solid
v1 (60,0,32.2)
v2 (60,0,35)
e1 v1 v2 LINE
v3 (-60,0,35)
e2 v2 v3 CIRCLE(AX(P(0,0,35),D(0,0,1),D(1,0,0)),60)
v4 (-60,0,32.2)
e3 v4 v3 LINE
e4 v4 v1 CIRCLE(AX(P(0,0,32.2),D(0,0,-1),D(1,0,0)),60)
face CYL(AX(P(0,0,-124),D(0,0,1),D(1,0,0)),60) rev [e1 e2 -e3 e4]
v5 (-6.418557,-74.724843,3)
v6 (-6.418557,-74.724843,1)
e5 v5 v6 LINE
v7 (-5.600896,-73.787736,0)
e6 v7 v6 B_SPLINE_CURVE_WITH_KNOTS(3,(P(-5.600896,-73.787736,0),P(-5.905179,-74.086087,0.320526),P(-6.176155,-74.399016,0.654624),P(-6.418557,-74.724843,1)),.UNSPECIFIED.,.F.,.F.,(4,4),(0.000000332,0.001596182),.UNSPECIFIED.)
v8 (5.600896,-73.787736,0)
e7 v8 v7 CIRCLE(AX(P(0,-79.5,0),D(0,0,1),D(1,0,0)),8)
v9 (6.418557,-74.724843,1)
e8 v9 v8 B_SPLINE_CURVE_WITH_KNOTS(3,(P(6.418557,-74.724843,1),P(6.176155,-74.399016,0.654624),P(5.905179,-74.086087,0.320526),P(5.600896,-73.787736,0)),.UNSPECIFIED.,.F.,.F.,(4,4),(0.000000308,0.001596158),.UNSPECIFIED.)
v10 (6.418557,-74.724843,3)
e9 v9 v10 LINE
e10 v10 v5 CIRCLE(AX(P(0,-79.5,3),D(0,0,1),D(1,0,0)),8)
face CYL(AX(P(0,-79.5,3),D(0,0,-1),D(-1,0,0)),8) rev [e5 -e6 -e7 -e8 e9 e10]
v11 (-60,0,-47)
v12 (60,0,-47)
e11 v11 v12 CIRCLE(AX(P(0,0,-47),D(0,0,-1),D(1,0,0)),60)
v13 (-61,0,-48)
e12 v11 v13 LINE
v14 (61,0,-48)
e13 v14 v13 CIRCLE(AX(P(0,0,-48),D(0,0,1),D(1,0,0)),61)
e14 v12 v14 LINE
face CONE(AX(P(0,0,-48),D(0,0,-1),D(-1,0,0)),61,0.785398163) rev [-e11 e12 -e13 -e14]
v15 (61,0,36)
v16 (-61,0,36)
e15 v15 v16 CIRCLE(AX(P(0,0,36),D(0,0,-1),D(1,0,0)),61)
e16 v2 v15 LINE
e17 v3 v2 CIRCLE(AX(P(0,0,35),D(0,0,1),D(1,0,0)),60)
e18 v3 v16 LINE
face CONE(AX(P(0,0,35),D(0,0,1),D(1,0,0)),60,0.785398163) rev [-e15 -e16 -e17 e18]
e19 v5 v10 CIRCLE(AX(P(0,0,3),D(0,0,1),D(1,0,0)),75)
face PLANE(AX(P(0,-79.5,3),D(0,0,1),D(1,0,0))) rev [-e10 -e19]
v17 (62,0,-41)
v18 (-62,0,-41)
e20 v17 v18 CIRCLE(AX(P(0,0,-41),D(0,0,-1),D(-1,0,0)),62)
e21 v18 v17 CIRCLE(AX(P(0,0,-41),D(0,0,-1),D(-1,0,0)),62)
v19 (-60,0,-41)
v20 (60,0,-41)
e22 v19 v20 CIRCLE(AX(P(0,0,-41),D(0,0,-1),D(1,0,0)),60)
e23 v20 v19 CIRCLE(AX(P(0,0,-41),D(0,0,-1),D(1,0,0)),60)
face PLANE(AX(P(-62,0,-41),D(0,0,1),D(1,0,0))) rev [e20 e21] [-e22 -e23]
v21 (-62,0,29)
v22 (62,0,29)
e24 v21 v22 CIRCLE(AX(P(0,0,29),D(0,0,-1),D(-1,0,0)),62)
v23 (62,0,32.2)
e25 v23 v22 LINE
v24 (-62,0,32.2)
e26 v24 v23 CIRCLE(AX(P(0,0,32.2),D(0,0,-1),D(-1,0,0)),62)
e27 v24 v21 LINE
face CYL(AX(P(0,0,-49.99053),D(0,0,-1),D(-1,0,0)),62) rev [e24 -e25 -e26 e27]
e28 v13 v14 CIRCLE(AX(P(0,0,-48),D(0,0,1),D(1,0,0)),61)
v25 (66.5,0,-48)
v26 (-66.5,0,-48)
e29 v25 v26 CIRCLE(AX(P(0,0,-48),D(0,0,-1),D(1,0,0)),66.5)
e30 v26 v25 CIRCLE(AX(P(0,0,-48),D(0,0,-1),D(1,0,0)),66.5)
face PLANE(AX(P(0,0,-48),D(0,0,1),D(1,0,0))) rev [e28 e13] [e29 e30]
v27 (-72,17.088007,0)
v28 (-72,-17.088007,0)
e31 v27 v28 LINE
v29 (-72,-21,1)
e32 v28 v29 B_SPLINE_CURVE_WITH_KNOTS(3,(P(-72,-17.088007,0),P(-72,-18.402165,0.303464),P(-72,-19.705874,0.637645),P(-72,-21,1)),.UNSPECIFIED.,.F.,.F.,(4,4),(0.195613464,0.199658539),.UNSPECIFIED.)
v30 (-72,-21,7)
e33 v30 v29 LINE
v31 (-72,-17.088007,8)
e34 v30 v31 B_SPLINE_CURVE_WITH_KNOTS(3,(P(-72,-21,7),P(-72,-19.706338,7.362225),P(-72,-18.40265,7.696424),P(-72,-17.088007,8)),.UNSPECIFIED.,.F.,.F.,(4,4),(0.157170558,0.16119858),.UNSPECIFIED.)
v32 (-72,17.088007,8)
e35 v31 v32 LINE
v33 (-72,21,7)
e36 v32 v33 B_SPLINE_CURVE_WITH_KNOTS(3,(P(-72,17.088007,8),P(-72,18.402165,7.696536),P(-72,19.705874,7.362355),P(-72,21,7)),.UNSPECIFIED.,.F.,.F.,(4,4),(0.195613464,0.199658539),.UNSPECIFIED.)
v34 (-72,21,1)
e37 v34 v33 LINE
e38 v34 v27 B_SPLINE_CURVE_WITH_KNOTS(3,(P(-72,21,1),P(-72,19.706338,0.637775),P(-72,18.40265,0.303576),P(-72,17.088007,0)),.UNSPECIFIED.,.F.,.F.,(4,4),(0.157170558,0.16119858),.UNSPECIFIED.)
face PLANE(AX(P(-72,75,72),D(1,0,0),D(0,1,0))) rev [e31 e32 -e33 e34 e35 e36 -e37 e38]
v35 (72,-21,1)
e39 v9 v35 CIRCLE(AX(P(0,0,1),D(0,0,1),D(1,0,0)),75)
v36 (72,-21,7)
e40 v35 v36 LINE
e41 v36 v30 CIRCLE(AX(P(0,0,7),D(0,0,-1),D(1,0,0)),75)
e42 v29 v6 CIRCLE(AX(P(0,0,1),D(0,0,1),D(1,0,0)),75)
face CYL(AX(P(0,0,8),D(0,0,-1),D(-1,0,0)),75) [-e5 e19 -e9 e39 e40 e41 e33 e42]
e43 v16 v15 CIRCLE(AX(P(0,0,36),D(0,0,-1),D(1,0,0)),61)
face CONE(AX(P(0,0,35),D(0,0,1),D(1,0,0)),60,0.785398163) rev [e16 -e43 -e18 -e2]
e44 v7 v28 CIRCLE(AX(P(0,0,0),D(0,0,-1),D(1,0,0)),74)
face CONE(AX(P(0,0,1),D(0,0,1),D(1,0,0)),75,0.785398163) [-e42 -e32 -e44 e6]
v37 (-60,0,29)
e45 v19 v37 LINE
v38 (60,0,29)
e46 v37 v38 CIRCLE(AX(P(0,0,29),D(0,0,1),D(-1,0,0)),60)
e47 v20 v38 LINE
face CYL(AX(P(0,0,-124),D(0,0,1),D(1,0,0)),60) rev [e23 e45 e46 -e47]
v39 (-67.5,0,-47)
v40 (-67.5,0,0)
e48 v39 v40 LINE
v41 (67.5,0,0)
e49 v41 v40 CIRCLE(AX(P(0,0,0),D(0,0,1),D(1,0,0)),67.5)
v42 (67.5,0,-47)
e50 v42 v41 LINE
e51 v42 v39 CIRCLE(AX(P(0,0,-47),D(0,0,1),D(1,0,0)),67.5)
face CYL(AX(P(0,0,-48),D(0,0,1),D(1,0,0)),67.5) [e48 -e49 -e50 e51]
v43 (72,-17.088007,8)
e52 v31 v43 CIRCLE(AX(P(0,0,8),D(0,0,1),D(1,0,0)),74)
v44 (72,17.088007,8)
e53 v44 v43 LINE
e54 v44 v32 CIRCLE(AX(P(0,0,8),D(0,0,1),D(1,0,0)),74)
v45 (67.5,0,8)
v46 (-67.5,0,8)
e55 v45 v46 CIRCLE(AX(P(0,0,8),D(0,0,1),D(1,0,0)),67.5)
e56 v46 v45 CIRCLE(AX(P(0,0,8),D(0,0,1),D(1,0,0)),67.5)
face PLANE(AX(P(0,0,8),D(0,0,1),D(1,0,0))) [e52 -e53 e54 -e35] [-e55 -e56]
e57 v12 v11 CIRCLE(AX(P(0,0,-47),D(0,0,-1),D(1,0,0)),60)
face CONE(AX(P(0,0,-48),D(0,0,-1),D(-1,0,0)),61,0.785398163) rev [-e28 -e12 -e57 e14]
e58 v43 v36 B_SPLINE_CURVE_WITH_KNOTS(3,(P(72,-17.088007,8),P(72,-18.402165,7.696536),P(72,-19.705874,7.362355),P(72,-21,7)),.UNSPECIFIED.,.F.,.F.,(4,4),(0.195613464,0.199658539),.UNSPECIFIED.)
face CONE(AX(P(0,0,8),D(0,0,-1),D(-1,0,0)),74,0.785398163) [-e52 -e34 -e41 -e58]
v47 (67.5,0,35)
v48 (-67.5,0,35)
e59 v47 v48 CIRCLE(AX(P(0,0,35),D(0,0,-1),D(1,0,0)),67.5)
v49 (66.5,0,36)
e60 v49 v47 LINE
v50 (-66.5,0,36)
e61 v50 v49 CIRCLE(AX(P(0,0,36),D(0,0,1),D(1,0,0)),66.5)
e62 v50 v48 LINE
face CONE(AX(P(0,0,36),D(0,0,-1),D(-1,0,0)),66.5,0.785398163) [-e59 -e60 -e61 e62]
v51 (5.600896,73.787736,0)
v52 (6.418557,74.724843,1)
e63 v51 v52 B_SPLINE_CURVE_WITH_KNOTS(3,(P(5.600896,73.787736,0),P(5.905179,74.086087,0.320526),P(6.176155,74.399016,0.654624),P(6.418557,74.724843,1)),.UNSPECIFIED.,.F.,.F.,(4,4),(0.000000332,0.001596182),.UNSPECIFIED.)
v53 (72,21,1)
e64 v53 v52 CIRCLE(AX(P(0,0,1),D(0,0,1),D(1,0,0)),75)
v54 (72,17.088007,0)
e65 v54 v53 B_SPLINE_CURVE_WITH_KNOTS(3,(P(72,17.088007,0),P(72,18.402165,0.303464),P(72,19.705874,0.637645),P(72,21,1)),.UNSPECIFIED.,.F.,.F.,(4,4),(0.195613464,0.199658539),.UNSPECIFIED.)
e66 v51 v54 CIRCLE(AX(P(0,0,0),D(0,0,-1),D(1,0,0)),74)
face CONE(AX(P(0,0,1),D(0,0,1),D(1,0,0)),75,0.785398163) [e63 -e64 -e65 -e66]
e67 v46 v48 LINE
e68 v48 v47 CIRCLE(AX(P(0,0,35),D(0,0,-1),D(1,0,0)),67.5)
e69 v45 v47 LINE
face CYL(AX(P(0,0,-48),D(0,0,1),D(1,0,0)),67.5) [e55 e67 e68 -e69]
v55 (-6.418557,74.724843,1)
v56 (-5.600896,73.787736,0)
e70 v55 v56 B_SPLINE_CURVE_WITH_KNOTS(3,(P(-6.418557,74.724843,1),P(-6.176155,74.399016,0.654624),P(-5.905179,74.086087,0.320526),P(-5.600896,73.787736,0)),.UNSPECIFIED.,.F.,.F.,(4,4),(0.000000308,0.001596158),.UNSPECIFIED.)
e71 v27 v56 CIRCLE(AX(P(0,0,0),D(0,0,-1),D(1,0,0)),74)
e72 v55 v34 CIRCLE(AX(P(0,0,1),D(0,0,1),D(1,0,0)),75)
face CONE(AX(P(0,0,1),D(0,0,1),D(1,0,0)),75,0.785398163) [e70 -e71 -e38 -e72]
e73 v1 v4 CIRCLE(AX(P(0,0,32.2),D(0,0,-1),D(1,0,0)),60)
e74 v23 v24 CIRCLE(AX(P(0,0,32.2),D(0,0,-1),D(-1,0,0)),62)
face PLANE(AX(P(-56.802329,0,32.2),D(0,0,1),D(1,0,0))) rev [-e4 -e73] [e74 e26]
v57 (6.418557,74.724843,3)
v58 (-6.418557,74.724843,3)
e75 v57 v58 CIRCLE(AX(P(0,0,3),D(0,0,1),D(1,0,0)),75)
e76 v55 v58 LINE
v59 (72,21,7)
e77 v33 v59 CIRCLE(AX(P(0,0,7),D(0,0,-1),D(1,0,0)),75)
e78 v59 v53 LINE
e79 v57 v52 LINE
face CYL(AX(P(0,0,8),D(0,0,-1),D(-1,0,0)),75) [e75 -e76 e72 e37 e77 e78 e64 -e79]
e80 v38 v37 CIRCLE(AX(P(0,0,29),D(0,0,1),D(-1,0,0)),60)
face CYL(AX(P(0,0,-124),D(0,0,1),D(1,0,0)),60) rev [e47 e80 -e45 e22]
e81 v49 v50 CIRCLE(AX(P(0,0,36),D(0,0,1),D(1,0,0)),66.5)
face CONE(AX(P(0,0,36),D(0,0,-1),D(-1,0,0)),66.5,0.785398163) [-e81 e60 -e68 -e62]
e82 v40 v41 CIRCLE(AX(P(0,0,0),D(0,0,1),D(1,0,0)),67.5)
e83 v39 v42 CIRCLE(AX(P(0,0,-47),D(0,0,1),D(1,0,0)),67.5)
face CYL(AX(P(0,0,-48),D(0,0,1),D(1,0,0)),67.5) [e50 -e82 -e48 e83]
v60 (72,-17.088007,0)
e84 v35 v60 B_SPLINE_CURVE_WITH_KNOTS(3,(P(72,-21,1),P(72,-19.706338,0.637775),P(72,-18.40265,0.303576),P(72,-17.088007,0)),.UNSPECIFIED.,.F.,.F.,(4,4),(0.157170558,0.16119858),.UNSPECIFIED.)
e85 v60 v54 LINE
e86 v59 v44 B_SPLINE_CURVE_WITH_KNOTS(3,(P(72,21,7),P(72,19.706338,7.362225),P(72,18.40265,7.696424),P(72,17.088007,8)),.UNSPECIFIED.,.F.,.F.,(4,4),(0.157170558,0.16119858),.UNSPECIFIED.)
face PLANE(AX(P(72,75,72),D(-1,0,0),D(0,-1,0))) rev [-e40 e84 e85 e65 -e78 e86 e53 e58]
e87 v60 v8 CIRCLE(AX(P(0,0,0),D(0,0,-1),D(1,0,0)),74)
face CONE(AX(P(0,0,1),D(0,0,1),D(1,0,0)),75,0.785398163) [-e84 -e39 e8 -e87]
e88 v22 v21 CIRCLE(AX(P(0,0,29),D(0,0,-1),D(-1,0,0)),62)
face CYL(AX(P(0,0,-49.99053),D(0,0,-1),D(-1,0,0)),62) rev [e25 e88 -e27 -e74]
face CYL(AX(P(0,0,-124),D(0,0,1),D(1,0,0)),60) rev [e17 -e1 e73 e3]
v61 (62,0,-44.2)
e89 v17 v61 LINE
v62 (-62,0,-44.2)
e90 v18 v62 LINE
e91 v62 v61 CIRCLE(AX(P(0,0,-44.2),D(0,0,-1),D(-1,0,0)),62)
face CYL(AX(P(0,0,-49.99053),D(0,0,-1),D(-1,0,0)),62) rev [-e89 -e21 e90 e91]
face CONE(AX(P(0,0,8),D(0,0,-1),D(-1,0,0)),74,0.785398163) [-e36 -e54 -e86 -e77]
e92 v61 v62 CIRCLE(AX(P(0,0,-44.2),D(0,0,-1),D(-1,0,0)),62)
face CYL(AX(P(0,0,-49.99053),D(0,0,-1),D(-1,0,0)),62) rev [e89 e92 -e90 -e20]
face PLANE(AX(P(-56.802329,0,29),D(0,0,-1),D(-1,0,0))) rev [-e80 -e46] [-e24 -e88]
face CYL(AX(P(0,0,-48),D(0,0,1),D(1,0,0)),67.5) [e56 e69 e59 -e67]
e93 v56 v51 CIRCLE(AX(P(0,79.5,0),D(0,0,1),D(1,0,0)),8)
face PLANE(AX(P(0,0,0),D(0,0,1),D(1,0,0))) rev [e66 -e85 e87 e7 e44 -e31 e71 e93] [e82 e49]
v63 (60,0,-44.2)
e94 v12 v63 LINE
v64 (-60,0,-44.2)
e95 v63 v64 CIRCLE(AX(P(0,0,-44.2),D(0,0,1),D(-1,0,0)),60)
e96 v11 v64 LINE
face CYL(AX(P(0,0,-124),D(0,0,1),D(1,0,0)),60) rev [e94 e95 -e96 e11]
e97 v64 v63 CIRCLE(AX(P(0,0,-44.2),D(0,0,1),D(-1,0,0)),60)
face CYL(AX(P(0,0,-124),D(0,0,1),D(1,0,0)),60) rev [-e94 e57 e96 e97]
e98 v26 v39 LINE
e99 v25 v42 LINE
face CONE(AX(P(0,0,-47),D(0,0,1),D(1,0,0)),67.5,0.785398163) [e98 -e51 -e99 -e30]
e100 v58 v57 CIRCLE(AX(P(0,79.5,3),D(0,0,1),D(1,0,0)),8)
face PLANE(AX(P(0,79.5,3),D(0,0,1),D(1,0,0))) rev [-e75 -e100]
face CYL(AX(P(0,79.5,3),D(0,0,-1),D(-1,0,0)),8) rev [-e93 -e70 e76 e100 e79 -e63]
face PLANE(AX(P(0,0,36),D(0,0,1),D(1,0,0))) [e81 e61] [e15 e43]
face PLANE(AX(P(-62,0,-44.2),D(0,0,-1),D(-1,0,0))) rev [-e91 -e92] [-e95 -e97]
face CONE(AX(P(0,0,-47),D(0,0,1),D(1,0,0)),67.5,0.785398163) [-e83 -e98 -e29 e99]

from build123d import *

# Parameters (mm, degrees)
SKETCH1_R                = 75
BOSS_EXTRUDE1_DEPTH      = 8
BOSS_EXTRUDE2_DEPTH      = 28
BOSS_EXTRUDE2_DEPTH_BACK = 56
SKETCH2_R                = 67.5
SKETCH3_R                = 60
CUT_EXTRUDE1_DEPTH       = 160
SKETCH4_W                = 5.197670867
SKETCH4_H                = 3.2
CHAMFER1_SIZE            = 1
SKETCH5_W                = 60
SKETCH5_H                = 150
CUT_EXTRUDE2_DEPTH       = 72
SKETCH6_R                = 8
CUT_EXTRUDE3_DEPTH       = 3


with BuildPart() as part:
    # Sketch1 → Boss-Extrude1 (new body)
    with BuildSketch(Plane.XY):
        Circle(SKETCH1_R)
    extrude(amount=BOSS_EXTRUDE1_DEPTH)

    # Sketch2 → Boss-Extrude2 (add, two sides: drawn at the far end of the back side and taken through both)
    with BuildSketch(Plane.XY.offset(8).offset(-BOSS_EXTRUDE2_DEPTH_BACK)):
        Circle(SKETCH2_R)
    extrude(amount=BOSS_EXTRUDE2_DEPTH + BOSS_EXTRUDE2_DEPTH_BACK)

    # Sketch3 → Cut-Extrude1 (cut)
    with BuildSketch(Plane.XY.offset(36)):
        Circle(SKETCH3_R)
    extrude(amount=-CUT_EXTRUDE1_DEPTH, mode=Mode.SUBTRACT)

    # Sketch4 → Cut-Revolve1 (revolve, cut)
    with BuildSketch(Plane(origin=(0, 0, 0), x_dir=(1, 0, 0), z_dir=(0, 1, 0)), mode=Mode.PRIVATE) as cut_revolve1_sk:
        with Locations((-59.401164567, -30.6)):
            Rectangle(SKETCH4_W, SKETCH4_H)
        with Locations((-59.401164567, 42.6)):
            Rectangle(SKETCH4_W, SKETCH4_H)
    revolve(cut_revolve1_sk.sketch.rotate(Axis((0, 0, -49.990530135), (0, 0, 1)), 180), axis=Axis((0, 0, -49.990530135), (0, 0, 1)), mode=Mode.SUBTRACT)

    # Chamfer1
    chamfer1_edges = [part.edges().sort_by_distance(p)[0] for p in [
        (-60, 0, -48),
        (-60, 0, 36),
        (-75, 0, 0),
        (-75, 0, 8),
        (-67.5, 0, -48),
        (-67.5, 0, 36),
    ]]
    chamfer(chamfer1_edges, length=CHAMFER1_SIZE)

    # Sketch5 → Cut-Extrude2 (cut)
    with BuildSketch(Plane(origin=(0, 0, 0), x_dir=(-1, 0, 0), z_dir=(0, 0, -1))):
        with Locations((-102, 0)):
            Rectangle(SKETCH5_W, SKETCH5_H)
        with Locations((102, 0)):
            Rectangle(SKETCH5_W, SKETCH5_H)
    extrude(amount=-CUT_EXTRUDE2_DEPTH, mode=Mode.SUBTRACT)

    # Sketch6 → Cut-Extrude3 (cut)
    with BuildSketch(Plane.XY):
        with Locations((0, 79.5)):
            Circle(SKETCH6_R)
        with Locations((0, -79.5)):
            Circle(SKETCH6_R)
    extrude(amount=CUT_EXTRUDE3_DEPTH, mode=Mode.SUBTRACT)


solid = part.part
